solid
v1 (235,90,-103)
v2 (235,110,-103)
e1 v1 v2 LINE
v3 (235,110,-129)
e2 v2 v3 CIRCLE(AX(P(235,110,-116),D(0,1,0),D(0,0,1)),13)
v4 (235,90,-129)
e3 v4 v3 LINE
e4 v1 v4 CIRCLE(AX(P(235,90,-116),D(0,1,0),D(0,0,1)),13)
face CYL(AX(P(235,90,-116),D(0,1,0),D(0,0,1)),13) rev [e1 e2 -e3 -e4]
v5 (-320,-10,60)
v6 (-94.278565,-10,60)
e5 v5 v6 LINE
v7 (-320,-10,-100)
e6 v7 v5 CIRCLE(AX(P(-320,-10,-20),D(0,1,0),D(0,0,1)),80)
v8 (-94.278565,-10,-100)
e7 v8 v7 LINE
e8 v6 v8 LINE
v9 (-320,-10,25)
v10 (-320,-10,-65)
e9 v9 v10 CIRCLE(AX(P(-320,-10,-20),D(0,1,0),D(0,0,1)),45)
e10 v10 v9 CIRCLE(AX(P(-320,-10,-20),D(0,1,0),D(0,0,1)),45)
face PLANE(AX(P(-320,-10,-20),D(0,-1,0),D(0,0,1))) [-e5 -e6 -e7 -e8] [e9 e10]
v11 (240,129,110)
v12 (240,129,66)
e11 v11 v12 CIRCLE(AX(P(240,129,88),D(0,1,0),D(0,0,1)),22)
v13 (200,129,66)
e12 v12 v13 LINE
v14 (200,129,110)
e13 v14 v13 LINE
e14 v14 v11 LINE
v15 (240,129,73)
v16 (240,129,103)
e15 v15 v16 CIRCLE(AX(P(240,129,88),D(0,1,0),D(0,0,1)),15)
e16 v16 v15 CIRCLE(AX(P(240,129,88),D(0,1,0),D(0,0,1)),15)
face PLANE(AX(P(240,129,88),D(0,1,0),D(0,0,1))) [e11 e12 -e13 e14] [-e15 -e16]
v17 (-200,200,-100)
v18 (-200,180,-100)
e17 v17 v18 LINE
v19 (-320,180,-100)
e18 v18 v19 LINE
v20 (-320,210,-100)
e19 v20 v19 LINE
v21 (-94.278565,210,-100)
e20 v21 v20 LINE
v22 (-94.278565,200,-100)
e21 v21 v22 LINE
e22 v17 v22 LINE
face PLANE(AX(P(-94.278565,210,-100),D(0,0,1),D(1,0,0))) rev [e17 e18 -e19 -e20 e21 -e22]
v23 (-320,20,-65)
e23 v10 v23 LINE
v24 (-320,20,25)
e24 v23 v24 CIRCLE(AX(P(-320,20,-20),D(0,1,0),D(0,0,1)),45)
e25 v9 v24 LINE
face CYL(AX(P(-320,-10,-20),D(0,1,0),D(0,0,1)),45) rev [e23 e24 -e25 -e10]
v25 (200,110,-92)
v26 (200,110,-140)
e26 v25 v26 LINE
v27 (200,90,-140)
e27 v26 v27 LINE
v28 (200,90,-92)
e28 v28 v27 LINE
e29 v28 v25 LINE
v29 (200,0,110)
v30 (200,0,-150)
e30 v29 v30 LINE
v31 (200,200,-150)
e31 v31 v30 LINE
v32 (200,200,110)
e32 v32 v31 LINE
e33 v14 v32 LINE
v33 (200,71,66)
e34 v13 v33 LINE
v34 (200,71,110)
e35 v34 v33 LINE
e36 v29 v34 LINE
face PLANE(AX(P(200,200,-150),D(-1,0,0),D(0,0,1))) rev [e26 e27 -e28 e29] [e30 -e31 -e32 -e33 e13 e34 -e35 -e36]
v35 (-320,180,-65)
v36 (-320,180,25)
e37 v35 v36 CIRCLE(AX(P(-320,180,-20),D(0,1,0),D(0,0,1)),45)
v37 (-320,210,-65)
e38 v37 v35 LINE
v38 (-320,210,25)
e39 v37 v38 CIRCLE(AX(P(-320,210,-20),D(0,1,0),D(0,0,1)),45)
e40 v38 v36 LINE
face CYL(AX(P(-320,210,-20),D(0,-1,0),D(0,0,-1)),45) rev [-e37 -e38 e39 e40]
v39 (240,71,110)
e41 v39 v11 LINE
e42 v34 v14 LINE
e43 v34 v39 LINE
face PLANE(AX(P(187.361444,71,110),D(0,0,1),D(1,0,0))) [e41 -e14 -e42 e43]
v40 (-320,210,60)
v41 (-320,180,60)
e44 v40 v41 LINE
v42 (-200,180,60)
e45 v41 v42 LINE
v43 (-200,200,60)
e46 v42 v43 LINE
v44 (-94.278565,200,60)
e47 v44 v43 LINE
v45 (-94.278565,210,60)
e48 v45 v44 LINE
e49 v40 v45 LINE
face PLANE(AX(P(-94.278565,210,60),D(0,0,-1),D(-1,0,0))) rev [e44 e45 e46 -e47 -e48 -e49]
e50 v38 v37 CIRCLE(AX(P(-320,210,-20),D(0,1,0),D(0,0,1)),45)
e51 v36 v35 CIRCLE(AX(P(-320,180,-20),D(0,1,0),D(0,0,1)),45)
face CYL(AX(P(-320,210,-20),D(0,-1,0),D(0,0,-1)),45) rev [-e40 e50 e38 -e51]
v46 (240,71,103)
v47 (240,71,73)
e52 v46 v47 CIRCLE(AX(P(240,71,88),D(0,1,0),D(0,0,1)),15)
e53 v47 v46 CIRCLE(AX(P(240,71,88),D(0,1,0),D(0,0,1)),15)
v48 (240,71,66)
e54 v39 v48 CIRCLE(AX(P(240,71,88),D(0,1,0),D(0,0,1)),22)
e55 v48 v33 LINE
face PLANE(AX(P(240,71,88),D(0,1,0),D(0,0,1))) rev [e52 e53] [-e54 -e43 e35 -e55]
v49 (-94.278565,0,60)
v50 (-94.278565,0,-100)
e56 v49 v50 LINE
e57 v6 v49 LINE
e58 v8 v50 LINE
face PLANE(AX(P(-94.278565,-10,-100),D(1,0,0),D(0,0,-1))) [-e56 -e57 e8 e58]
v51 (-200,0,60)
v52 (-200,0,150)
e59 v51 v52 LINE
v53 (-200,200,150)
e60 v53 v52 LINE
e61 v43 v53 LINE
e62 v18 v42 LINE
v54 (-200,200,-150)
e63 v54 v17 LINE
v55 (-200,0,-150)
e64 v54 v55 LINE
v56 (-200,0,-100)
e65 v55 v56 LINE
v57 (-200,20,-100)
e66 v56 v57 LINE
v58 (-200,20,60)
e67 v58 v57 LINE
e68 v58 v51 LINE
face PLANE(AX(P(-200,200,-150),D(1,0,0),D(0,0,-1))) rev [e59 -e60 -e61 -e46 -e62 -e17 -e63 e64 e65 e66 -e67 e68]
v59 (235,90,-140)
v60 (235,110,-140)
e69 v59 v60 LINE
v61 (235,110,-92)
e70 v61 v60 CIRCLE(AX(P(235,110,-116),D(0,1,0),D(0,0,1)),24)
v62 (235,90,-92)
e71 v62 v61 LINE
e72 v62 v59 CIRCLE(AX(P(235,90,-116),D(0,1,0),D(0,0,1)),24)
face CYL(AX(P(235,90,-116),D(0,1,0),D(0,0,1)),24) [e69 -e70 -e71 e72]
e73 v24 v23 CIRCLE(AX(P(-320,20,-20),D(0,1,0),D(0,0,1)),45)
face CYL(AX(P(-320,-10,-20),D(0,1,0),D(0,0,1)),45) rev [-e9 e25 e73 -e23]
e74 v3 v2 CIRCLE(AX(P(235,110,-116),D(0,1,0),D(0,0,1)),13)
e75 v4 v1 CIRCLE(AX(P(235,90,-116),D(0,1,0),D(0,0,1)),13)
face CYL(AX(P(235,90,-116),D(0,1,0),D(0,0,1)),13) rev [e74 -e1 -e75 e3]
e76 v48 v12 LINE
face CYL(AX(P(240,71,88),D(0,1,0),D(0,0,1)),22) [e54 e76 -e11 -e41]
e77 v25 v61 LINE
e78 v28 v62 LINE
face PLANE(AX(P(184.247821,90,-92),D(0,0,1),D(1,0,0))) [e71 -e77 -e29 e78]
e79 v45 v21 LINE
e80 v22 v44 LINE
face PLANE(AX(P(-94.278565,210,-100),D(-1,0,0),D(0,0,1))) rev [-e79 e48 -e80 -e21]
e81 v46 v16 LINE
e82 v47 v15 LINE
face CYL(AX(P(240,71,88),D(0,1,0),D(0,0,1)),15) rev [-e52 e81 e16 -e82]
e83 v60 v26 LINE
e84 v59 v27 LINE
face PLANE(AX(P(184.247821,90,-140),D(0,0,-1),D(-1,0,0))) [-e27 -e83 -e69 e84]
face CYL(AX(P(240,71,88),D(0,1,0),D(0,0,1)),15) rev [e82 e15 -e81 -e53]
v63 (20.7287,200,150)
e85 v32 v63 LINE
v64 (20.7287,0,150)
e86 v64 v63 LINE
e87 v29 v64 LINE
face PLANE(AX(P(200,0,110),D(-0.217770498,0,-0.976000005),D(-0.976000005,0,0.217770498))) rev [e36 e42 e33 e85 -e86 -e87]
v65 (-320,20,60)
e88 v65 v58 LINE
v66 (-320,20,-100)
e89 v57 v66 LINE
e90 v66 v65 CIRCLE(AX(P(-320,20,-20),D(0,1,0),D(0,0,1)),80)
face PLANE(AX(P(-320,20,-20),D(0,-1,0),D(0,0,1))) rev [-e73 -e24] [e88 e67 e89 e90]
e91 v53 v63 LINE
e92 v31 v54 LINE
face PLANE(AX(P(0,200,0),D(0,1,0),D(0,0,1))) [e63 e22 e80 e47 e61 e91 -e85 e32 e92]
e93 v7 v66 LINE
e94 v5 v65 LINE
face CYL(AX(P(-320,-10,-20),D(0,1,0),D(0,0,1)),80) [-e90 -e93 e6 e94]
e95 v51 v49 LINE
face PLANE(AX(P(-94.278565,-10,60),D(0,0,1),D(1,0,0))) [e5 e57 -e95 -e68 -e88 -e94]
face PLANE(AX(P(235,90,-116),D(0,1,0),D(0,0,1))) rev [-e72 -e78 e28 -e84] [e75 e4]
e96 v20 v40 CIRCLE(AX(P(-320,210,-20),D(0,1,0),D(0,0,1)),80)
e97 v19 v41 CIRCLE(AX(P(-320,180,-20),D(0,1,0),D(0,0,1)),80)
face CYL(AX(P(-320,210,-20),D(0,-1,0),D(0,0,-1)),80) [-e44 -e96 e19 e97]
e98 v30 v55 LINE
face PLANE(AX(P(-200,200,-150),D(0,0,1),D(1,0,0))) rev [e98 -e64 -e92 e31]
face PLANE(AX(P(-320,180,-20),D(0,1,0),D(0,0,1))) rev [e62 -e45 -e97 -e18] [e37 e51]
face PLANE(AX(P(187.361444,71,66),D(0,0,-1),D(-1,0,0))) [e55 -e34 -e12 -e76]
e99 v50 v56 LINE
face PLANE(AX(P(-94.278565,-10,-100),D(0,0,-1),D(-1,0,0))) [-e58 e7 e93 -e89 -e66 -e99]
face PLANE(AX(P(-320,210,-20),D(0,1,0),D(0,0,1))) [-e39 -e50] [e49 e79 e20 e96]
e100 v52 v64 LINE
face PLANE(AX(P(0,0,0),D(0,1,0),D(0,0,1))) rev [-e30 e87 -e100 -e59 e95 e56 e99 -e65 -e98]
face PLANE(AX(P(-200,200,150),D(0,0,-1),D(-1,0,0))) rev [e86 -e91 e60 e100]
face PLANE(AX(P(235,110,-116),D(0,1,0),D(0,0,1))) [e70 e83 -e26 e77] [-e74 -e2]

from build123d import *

# Parameters (mm, degrees)
SKETCH1_W                = 400
SKETCH1_H                = 300
BOSS_EXTRUDE1_DEPTH      = 200
BOSS_EXTRUDE2_DEPTH      = 29
BOSS_EXTRUDE2_DEPTH_BACK = 29
SKETCH2_R                = 15
CUT_EXTRUDE1_DEPTH       = 363.138095207
BOSS_EXTRUDE3_START      = -20
SKETCH4_R                = 45
BOSS_EXTRUDE3_DEPTH      = 30
BOSS_EXTRUDE4_DEPTH      = 10
BOSS_EXTRUDE4_DEPTH_BACK = 10
SKETCH5_R                = 13


with BuildPart() as part:
    # Sketch1 → Boss-Extrude1 (new body)
    with BuildSketch(Plane(origin=(0, 0, 0), x_dir=(1, 0, 0), z_dir=(0, 1, 0))):
        Rectangle(SKETCH1_W, SKETCH1_H)
    extrude(amount=BOSS_EXTRUDE1_DEPTH)

    # Sketch2 → Boss-Extrude2 (add, two sides: drawn at the far end of the back side and taken through both)
    with BuildSketch(Plane(origin=(0, 100, 0), x_dir=(1, 0, 0), z_dir=(0, 1, 0)).offset(-BOSS_EXTRUDE2_DEPTH_BACK)):
        with BuildLine():
            Line((187.36144438, -66), (240, -66))
            ThreePointArc((240, -66), (262, -88), (240, -110))
            Line((240, -110), (187.36144438, -110))
            Line((187.36144438, -110), (187.36144438, -66))
        make_face()
        with Locations(Location((240, -88, 0), (0, 0, 270))):
            Circle(SKETCH2_R, mode=Mode.SUBTRACT)
    extrude(amount=BOSS_EXTRUDE2_DEPTH + BOSS_EXTRUDE2_DEPTH_BACK)

    # Sketch3 → Cut-Extrude1 (cut, through all)
    with BuildSketch(Plane(origin=(0, 200, 0), x_dir=(1, 0, 0), z_dir=(0, 1, 0))):
        Polygon((200, -110), (20.728700198, -150), (200, -150), align=None)
    extrude(amount=-CUT_EXTRUDE1_DEPTH, mode=Mode.SUBTRACT)

    # Sketch4 → Boss-Extrude3 (add)
    with BuildSketch(Plane(origin=(0, 200, 0), x_dir=(1, 0, 0), z_dir=(0, 1, 0)).offset(BOSS_EXTRUDE3_START)):
        with BuildLine():
            Line((-94.278565111, -60), (-320, -60))
            ThreePointArc((-320, -60), (-400, 20), (-320, 100))
            Line((-320, 100), (-94.278565111, 100))
            Line((-94.278565111, 100), (-94.278565111, -60))
        make_face()
        with Locations(Location((-320, 20, 0), (0, 0, 270))):
            Circle(SKETCH4_R, mode=Mode.SUBTRACT)
    boss_extrude3 = extrude(amount=BOSS_EXTRUDE3_DEPTH)

    # Mirror1: Boss-Extrude3 across plane
    add(boss_extrude3.mirror(Plane.ZX.offset(100)))

    # Sketch5 → Boss-Extrude4 (add, two sides: drawn at the far end of the back side and taken through both)
    with BuildSketch(Plane(origin=(0, 100, 0), x_dir=(1, 0, 0), z_dir=(0, 1, 0)).offset(-BOSS_EXTRUDE4_DEPTH_BACK)):
        with BuildLine():
            Line((184.247820943, 140), (235, 140))
            ThreePointArc((235, 140), (259, 116), (235, 92))
            Line((235, 92), (184.247820943, 92))
            Line((184.247820943, 92), (184.247820943, 140))
        make_face()
        with Locations(Location((235, 116, 0), (0, 0, 270))):
            Circle(SKETCH5_R, mode=Mode.SUBTRACT)
    extrude(amount=BOSS_EXTRUDE4_DEPTH + BOSS_EXTRUDE4_DEPTH_BACK)


solid = part.part
